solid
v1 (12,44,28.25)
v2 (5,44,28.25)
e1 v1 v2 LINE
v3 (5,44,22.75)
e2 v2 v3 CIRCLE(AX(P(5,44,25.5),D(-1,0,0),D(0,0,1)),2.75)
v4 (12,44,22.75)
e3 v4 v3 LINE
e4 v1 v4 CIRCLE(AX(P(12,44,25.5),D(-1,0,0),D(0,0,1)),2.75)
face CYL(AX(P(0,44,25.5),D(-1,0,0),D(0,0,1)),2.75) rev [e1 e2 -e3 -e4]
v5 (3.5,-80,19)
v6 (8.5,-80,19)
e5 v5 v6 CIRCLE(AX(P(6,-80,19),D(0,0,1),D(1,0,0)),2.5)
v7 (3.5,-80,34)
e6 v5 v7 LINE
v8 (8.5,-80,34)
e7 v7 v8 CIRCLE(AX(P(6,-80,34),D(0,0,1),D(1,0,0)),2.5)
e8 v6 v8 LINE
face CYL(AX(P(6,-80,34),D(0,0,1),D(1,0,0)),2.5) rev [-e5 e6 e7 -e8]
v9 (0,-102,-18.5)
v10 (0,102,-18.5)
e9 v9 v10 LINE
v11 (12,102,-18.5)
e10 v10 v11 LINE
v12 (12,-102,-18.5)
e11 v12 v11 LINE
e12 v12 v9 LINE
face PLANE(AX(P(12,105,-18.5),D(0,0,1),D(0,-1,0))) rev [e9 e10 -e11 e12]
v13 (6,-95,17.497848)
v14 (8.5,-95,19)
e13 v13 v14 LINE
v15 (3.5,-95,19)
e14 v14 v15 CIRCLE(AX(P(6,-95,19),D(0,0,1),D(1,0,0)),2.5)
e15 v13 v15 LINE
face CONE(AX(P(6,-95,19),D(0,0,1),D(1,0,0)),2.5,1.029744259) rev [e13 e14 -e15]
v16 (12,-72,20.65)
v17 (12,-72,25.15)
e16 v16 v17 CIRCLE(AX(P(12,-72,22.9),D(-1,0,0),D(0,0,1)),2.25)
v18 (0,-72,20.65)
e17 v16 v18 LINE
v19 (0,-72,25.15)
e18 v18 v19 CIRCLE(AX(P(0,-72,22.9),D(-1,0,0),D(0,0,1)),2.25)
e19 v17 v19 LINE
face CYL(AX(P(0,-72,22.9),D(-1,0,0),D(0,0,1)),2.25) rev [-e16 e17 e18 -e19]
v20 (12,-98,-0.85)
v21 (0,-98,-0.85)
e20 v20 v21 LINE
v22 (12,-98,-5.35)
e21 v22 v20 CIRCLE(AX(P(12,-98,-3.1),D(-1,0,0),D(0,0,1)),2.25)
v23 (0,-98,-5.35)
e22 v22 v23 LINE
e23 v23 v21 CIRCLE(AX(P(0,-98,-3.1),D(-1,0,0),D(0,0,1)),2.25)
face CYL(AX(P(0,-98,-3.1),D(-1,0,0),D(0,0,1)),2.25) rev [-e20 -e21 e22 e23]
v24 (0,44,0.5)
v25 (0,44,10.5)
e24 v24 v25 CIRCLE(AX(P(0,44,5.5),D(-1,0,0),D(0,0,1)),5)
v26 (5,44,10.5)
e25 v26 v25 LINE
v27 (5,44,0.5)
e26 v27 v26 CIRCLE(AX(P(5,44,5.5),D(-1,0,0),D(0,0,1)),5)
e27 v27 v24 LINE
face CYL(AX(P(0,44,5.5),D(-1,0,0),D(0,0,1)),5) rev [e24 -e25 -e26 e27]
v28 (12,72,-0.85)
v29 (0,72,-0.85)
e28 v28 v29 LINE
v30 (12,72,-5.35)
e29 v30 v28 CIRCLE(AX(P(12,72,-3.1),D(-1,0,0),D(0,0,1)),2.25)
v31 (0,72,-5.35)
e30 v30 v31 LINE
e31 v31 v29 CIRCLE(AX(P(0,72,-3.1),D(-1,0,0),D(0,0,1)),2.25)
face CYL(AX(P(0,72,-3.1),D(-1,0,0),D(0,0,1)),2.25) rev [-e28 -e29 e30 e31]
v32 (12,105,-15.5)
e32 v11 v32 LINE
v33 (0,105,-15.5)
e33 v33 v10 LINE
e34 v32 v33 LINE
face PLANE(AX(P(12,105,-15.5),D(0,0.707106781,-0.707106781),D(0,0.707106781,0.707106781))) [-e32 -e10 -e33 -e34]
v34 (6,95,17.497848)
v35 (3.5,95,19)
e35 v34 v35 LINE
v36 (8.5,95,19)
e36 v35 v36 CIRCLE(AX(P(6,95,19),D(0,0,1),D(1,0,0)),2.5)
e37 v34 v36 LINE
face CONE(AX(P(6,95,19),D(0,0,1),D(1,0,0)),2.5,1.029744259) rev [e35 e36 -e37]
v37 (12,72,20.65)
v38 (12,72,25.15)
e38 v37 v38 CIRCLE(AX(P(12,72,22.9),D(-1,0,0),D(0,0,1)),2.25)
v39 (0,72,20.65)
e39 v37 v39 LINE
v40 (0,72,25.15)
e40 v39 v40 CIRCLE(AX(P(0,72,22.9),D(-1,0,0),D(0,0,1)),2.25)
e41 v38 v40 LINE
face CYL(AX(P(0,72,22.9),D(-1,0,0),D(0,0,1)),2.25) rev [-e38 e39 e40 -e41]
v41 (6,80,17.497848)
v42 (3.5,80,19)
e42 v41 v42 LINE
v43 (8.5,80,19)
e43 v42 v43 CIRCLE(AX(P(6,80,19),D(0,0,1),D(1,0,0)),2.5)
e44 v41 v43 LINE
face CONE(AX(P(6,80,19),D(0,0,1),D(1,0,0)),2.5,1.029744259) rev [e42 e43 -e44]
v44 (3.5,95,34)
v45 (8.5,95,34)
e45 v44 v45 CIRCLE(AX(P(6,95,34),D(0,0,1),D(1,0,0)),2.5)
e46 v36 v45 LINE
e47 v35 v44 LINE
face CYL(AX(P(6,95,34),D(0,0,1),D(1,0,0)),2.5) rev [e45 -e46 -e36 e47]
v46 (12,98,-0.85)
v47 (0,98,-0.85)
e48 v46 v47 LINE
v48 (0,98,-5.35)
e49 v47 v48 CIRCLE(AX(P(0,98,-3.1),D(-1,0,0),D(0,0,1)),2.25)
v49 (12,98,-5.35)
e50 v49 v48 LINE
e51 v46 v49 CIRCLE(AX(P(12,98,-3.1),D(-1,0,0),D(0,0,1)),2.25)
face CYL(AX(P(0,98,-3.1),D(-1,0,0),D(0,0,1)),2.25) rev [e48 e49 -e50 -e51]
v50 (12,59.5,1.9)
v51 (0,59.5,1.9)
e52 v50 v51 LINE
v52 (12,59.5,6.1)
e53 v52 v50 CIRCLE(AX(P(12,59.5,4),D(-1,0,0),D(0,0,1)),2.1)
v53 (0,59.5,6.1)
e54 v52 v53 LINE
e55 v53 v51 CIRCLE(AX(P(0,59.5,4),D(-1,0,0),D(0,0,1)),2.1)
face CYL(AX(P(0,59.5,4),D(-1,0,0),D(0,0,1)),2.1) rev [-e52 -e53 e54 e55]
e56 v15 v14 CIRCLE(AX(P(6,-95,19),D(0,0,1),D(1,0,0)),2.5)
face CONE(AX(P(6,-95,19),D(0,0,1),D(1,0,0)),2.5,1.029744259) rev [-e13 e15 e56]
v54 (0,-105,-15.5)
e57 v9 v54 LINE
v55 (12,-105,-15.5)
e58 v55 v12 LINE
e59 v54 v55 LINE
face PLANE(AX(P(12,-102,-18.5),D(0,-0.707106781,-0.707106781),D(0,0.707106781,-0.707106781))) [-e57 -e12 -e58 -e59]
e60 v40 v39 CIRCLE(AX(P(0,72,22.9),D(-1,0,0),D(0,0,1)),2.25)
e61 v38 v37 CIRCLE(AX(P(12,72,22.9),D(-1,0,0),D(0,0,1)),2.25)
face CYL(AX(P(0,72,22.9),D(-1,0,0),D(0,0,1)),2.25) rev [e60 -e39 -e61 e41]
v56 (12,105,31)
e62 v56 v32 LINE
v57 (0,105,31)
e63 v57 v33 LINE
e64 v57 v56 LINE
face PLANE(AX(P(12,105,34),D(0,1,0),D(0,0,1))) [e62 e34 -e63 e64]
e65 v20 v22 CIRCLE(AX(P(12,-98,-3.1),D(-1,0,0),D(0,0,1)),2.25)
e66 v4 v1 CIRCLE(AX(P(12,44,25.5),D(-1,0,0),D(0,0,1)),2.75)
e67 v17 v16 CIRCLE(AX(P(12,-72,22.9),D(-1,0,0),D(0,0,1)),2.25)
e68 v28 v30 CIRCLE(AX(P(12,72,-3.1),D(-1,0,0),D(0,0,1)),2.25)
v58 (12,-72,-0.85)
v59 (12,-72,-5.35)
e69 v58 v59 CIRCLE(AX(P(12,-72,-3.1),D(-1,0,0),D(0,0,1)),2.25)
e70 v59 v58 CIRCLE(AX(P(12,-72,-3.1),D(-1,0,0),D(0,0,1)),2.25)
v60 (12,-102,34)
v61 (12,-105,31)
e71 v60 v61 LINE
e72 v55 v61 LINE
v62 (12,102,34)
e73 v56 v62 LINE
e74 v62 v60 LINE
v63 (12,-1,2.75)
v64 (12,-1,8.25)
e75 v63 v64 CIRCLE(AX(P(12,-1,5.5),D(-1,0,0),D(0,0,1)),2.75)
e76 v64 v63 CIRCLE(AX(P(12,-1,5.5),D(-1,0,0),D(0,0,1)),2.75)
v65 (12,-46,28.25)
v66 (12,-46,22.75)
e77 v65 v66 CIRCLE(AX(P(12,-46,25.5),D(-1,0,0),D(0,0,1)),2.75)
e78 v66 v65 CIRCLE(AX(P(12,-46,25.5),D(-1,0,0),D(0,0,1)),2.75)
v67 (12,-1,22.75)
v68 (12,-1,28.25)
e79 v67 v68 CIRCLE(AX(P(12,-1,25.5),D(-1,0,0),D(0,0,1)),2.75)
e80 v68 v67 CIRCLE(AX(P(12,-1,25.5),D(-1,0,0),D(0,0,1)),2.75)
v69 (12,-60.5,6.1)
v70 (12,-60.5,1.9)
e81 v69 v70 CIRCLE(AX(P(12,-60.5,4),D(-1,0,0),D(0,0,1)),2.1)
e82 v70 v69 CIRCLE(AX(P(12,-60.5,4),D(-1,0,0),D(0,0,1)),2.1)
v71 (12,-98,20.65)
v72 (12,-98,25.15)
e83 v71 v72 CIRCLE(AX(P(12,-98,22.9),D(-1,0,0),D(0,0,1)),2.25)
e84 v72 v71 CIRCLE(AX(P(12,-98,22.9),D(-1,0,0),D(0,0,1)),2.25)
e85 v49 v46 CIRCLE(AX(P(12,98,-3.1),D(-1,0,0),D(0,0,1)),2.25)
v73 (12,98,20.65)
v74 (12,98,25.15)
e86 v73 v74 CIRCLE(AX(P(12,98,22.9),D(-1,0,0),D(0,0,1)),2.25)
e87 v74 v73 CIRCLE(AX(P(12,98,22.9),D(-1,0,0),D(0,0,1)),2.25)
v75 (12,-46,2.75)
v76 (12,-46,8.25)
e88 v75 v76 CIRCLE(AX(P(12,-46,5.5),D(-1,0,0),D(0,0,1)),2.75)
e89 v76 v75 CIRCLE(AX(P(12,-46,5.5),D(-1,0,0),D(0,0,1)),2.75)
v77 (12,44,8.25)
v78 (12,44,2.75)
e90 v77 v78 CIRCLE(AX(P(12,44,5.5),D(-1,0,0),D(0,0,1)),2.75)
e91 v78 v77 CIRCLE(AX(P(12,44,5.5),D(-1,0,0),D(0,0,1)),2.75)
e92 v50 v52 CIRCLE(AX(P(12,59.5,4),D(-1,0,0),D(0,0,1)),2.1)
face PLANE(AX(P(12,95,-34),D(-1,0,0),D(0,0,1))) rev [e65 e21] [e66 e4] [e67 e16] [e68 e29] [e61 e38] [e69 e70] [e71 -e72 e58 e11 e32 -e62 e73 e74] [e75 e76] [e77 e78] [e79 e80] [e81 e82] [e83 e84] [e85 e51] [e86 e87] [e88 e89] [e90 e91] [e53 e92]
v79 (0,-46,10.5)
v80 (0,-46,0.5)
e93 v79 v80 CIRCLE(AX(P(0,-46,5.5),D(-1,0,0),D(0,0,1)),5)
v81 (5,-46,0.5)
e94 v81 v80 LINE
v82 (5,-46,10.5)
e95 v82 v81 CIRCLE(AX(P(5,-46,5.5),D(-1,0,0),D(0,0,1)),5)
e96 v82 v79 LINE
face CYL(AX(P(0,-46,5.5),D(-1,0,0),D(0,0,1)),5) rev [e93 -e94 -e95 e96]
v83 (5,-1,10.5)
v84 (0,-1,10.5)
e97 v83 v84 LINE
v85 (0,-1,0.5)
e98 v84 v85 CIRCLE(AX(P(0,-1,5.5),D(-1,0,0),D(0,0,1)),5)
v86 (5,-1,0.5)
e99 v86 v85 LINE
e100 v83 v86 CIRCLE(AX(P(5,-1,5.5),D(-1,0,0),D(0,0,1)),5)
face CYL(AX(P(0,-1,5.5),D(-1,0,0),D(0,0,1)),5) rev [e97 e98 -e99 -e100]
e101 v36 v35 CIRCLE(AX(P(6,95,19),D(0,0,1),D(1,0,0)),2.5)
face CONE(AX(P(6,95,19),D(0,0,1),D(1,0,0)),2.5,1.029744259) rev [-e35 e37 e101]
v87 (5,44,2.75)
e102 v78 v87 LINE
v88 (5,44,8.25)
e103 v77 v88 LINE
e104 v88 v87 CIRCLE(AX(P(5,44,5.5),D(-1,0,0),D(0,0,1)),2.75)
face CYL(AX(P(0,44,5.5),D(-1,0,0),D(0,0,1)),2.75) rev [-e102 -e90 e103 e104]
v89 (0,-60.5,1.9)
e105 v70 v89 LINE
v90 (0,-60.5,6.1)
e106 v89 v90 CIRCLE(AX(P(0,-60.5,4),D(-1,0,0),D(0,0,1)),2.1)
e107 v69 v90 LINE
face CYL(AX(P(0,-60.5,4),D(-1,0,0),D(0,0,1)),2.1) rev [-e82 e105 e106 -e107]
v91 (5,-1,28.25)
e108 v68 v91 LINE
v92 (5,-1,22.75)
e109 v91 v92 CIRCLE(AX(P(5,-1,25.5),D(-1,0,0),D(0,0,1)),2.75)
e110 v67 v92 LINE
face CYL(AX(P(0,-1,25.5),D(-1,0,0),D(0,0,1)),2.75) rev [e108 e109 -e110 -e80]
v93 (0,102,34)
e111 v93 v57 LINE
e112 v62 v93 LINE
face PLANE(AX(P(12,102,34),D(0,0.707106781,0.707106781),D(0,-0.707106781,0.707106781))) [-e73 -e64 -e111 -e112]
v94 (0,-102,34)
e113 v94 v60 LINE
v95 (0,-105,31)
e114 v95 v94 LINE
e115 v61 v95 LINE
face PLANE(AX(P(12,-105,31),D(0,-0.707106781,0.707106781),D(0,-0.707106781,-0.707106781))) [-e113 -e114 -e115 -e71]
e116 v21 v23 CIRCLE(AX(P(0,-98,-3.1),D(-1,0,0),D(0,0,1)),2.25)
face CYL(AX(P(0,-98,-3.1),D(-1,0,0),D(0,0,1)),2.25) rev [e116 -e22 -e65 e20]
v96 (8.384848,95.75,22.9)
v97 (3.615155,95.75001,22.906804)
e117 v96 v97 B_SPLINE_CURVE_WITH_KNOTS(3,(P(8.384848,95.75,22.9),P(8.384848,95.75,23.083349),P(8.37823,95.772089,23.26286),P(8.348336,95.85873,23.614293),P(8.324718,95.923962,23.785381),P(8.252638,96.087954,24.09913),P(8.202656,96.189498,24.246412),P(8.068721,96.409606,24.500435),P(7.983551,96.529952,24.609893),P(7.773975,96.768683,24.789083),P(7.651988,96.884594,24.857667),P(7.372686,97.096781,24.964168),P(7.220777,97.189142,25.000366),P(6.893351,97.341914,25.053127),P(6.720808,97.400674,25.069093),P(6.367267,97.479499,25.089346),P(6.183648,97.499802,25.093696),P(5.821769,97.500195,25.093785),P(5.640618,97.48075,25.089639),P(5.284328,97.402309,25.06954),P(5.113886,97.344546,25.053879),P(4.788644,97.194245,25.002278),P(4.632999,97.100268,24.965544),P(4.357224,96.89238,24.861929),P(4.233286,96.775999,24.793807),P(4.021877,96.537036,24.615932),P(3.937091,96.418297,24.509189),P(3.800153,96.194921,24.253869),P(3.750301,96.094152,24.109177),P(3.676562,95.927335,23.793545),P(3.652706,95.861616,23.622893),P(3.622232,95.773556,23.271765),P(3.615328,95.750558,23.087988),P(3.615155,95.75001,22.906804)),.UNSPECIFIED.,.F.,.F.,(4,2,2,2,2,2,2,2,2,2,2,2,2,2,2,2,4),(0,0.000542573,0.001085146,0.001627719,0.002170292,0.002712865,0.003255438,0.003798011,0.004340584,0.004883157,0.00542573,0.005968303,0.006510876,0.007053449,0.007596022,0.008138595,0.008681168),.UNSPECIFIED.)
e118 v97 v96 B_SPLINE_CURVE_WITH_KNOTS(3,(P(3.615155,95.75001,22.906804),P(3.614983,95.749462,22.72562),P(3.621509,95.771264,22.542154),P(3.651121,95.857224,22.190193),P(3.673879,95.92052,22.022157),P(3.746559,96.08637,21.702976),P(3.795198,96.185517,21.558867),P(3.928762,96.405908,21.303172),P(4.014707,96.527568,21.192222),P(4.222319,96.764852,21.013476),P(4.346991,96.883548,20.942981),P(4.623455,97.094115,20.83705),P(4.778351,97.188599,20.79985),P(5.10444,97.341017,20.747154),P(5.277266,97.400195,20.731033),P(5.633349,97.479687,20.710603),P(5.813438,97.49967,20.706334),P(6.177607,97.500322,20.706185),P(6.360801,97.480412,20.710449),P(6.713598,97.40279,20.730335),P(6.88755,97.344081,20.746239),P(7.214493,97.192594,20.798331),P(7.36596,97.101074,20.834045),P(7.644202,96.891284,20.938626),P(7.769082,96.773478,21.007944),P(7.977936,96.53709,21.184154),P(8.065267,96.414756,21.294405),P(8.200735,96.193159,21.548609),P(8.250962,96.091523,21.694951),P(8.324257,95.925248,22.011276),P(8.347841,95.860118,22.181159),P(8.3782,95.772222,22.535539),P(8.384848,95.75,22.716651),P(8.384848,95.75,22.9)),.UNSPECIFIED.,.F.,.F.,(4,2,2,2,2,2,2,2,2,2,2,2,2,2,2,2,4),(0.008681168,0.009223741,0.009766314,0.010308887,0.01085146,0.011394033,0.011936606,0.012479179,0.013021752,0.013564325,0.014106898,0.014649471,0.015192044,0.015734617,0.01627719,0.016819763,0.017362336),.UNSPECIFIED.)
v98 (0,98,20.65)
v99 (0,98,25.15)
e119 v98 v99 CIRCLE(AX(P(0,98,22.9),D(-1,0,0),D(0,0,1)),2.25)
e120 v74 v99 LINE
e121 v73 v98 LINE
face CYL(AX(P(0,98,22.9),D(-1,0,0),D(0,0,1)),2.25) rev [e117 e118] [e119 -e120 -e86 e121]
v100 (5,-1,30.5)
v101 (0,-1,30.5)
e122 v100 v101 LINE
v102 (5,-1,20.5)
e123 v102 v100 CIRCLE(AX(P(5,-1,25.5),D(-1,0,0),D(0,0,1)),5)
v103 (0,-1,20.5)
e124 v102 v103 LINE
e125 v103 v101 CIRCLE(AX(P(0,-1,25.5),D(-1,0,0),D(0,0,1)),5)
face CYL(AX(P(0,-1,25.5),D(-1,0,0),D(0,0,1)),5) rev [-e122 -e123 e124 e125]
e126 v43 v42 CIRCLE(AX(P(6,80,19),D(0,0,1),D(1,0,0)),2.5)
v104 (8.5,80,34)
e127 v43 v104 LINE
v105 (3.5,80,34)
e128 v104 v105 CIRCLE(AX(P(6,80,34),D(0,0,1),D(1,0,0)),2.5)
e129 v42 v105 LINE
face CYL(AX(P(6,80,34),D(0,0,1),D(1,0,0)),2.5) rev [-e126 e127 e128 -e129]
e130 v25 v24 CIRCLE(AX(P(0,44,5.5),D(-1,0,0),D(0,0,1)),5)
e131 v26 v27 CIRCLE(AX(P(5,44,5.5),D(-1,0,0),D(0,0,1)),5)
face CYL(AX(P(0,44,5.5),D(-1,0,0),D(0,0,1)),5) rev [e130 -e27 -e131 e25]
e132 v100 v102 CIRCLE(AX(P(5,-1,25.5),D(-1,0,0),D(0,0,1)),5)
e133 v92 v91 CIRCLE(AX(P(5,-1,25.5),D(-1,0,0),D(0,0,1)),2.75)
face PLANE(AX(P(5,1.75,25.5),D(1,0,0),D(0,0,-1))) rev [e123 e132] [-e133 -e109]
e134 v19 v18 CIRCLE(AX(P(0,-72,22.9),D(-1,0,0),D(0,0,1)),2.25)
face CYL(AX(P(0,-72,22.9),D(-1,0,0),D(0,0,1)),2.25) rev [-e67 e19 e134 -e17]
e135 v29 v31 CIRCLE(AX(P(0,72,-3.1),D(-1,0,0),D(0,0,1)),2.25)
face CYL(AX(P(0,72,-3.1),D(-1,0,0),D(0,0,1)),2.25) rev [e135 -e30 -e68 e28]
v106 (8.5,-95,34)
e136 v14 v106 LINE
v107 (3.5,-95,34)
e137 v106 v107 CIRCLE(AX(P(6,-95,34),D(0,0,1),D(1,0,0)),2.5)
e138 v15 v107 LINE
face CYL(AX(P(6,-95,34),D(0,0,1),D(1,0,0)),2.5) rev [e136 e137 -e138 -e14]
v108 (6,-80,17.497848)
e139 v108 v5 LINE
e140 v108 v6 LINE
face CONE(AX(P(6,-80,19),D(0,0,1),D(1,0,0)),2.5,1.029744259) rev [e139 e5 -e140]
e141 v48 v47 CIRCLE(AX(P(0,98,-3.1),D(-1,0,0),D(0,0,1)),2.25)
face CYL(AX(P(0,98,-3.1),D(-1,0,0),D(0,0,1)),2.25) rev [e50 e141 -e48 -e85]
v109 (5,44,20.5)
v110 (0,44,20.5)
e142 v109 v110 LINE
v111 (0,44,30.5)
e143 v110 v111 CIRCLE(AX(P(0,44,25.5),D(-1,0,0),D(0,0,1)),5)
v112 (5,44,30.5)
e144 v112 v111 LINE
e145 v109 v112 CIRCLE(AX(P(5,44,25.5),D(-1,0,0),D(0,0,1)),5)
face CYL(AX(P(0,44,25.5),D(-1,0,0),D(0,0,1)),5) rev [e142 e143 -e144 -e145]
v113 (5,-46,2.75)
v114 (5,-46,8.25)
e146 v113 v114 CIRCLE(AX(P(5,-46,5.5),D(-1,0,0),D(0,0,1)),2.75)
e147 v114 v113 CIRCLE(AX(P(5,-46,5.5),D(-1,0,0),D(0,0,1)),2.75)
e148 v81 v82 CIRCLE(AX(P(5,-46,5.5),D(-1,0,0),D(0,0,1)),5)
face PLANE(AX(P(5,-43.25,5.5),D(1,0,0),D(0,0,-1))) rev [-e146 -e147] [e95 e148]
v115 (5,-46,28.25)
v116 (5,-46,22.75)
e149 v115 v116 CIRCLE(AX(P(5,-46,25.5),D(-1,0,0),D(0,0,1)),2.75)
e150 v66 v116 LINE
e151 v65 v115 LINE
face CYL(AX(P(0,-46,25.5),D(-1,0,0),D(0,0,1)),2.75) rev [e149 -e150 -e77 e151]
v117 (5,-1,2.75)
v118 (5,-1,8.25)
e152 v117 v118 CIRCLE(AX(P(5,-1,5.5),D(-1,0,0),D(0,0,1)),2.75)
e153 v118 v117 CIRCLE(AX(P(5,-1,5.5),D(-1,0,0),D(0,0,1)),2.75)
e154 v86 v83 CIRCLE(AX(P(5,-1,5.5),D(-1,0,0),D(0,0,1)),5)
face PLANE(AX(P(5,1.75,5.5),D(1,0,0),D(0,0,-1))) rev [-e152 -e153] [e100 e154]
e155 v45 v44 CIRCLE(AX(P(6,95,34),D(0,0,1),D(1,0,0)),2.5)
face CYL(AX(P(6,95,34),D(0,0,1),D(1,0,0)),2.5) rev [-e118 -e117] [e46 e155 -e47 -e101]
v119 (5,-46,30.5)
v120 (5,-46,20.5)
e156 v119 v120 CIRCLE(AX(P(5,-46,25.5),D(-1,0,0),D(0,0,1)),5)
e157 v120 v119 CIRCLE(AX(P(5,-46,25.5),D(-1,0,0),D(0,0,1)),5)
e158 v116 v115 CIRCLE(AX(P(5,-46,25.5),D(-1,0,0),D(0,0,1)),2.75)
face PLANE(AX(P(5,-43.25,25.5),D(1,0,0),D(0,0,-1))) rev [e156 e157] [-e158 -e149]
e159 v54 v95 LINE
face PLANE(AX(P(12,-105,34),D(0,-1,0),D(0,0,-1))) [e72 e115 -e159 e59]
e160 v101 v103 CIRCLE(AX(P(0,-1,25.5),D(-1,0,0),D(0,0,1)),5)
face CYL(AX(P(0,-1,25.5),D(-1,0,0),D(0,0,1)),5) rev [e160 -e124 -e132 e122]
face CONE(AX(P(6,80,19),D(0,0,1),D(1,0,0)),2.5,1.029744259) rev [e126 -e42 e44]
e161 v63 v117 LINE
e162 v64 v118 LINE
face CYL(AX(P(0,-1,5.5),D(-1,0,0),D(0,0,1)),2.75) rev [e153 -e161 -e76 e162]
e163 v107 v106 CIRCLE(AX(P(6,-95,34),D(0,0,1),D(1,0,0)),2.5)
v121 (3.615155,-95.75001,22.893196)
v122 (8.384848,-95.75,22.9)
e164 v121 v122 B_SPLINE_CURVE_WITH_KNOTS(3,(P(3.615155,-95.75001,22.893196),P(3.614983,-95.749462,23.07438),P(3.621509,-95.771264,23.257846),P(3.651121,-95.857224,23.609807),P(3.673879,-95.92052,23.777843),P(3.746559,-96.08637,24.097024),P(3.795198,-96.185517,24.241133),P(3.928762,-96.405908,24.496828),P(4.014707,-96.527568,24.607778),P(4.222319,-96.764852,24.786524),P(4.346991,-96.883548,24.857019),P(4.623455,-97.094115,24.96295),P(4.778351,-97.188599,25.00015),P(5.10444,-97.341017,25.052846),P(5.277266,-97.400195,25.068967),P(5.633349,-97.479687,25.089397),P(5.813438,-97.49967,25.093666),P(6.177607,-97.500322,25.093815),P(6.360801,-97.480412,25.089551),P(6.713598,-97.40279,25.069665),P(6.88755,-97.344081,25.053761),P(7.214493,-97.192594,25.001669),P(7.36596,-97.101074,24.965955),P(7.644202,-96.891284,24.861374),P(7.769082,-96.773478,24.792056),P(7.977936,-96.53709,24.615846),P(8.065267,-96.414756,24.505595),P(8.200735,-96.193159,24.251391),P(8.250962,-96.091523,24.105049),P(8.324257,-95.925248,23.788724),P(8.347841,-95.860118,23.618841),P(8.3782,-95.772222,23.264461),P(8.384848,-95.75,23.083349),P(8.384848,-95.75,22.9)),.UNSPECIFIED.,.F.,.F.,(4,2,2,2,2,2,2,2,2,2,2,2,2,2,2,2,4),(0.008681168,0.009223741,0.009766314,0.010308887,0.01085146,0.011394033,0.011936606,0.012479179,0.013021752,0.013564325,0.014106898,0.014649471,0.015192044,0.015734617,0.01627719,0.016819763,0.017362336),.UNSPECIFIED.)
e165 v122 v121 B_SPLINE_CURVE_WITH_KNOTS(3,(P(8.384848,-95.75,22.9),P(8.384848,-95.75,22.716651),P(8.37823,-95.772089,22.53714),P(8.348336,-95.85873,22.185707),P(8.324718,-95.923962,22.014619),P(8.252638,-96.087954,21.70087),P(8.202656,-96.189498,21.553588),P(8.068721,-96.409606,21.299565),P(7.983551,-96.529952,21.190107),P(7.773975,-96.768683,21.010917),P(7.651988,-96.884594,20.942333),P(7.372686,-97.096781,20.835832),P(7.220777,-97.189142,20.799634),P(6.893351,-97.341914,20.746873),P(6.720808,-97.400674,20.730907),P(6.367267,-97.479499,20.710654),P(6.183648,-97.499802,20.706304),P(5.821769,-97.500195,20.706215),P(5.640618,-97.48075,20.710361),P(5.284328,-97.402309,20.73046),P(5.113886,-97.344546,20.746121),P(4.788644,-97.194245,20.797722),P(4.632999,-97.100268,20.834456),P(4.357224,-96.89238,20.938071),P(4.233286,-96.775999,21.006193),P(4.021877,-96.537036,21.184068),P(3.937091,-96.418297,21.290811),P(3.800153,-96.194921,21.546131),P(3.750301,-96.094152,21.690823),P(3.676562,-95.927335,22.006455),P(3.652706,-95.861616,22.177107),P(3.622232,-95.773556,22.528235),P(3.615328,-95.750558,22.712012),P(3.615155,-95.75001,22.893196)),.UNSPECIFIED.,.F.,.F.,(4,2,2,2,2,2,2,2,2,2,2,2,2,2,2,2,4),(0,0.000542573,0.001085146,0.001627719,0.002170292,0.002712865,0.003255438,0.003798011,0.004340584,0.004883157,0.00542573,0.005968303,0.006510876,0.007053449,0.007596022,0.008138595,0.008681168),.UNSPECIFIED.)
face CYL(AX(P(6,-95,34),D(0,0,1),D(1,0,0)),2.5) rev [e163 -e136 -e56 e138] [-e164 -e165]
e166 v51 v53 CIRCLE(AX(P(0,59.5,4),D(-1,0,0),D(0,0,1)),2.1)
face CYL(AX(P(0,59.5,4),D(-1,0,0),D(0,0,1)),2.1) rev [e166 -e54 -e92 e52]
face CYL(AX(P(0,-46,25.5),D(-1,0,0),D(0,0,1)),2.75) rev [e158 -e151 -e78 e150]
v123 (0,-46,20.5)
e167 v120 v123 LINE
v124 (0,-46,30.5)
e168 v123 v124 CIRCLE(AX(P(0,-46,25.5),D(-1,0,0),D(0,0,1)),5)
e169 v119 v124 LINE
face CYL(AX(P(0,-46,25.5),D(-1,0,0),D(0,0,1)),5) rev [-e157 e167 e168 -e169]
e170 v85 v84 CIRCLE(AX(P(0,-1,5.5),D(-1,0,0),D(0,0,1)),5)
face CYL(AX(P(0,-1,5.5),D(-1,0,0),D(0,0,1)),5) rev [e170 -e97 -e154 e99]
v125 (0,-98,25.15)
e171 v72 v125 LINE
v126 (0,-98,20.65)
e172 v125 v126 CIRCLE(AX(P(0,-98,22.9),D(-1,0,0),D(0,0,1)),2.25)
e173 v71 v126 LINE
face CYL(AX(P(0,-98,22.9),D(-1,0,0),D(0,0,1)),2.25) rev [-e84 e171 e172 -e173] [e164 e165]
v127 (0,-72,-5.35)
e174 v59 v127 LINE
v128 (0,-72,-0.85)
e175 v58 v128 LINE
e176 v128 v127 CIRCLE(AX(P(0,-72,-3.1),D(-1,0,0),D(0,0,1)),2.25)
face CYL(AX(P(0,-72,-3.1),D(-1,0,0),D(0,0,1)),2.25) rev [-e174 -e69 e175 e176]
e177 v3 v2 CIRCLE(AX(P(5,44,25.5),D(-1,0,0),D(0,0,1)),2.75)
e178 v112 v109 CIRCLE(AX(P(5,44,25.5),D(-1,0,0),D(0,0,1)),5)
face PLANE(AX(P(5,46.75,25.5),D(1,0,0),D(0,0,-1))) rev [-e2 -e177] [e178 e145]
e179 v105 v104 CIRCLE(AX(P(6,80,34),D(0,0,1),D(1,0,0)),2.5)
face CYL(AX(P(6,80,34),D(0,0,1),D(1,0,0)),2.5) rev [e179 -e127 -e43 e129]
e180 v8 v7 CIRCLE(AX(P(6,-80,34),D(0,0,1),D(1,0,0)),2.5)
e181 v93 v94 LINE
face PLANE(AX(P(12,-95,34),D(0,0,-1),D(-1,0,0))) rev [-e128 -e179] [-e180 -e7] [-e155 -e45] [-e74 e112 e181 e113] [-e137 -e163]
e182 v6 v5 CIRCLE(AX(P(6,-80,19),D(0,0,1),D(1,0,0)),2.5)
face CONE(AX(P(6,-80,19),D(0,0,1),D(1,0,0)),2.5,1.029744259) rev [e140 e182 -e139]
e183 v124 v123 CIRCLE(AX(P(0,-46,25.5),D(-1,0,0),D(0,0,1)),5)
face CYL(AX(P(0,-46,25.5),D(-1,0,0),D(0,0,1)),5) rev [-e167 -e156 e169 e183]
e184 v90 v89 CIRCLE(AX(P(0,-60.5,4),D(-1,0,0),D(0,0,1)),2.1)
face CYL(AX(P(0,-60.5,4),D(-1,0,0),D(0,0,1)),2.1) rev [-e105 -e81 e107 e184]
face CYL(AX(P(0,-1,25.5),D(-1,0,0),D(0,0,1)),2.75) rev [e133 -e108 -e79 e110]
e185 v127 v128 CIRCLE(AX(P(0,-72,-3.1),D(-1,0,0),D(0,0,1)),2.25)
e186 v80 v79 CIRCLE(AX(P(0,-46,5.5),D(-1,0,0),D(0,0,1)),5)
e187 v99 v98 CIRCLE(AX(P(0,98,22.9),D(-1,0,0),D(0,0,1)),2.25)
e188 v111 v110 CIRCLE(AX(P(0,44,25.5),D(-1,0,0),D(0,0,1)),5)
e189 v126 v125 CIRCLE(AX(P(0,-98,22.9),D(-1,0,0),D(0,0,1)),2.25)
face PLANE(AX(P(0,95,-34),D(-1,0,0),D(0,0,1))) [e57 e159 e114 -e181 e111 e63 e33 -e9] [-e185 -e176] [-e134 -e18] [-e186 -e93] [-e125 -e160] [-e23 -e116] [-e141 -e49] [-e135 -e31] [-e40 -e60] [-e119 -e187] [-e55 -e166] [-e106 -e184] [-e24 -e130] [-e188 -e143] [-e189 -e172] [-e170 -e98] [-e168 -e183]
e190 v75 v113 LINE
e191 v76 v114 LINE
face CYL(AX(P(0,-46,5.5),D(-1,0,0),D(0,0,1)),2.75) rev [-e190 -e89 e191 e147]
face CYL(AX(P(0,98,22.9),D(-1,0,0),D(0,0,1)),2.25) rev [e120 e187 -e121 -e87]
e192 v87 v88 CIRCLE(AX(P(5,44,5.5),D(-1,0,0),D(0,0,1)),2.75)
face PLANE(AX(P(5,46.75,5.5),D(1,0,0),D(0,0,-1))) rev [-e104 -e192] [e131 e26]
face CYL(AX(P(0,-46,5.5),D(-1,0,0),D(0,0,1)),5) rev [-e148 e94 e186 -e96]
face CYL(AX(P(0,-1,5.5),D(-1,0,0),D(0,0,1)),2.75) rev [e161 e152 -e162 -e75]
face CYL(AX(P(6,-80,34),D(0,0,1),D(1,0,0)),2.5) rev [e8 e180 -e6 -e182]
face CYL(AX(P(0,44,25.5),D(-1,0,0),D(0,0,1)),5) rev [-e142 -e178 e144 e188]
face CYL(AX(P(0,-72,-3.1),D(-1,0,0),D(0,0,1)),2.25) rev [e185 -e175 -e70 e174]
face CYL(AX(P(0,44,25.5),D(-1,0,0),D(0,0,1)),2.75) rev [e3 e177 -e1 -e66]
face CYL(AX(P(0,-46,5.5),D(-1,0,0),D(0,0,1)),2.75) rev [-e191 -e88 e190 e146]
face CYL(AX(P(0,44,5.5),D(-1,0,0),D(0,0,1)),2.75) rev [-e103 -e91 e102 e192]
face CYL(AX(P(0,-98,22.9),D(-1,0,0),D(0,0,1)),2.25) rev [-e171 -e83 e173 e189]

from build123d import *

# Parameters (mm, degrees)
SKETCH_1_W                                         = 68
SKETCH_1_H                                         = 190
BOSS_EXTRUDE_1_DEPTH                               = 12
SKETCH_9_W                                         = 68
SKETCH_9_H                                         = 10
BOSS_EXTRUDE_2_DEPTH                               = 12
F_4_5_4_5_HOLE_1_D                                 = 4.5
LINEAR_PATTERN_2_COUNT                             = 2
LINEAR_PATTERN_2_PITCH                             = 26
LINEAR_PATTERN_2_COUNT_DIR2                        = 2
LINEAR_PATTERN_2_PITCH_DIR2                        = 26
M5_SOCKET_HEAD_CAP_SCREW_COUNTERBORE_1_D           = 5.5
M5_SOCKET_HEAD_CAP_SCREW_COUNTERBORE_1_CBORE_D     = 10
M5_SOCKET_HEAD_CAP_SCREW_COUNTERBORE_1_CBORE_DEPTH = 5
LINEAR_PATTERN_3_COUNT                             = 3
LINEAR_PATTERN_3_PITCH                             = 45
LINEAR_PATTERN_3_COUNT_DIR2                        = 2
LINEAR_PATTERN_3_PITCH_DIR2                        = 20
SKETCH_14_W                                        = 20
SKETCH_14_H                                        = 215
CUT_EXTRUDE_4_DEPTH                                = 112.018016556
LINEAR_PATTERN_4_COUNT                             = 2
LINEAR_PATTERN_4_PITCH                             = 170
LINEAR_PATTERN_4_COPY_1_D                          = 4.5
LINEAR_PATTERN_4_COPY_2_D                          = 4.5
LINEAR_PATTERN_4_COPY_3_D                          = 4.5
M5_TAPPED_HOLE_1_D                                 = 4.2
LINEAR_PATTERN_5_COUNT                             = 2
LINEAR_PATTERN_5_PITCH                             = 120
LINEAR_PATTERN_6_COUNT                             = 2
LINEAR_PATTERN_6_PITCH                             = 15
CHAMFER_1_SIZE                                     = 3


with BuildPart() as part:
    # Sketch 1 → Boss-Extrude 1 (new body)
    with BuildSketch(Plane(origin=(0, 0, 0), x_dir=(0, 0, -1), z_dir=(1, 0, 0))):
        Rectangle(SKETCH_1_W, SKETCH_1_H)
    extrude(amount=BOSS_EXTRUDE_1_DEPTH)

    # Sketch 9 → Boss-Extrude 2 (add)
    with BuildSketch(Plane.ZY):
        with Locations((0, 100)):
            Rectangle(SKETCH_9_W, SKETCH_9_H)
        with Locations((0, -100)):
            Rectangle(SKETCH_9_W, SKETCH_9_H)
    extrude(amount=-BOSS_EXTRUDE_2_DEPTH)

    # Ø4.5 (4.5) Hole 1 (through all)
    with Locations(Plane.ZY):
        with Locations((22.9, -98)):
            f_4_5_4_5_hole_1 = Hole(F_4_5_4_5_HOLE_1_D / 2)

    # Linear Pattern 2: 4.5 _4.5_ Hole 1 2 × 2
    with Locations(*[(0, i * LINEAR_PATTERN_2_PITCH, -j * LINEAR_PATTERN_2_PITCH_DIR2) for i in range(LINEAR_PATTERN_2_COUNT) for j in range(LINEAR_PATTERN_2_COUNT_DIR2) if (i, j) != (0, 0)]):
        add(f_4_5_4_5_hole_1, mode=Mode.SUBTRACT)

    # M5 Socket Head Cap Screw Counterbore 1 (through all)
    with Locations(Plane.ZY):
        with Locations((5.5, 44)):
            m5_socket_head_cap_screw_counterbore_1 = CounterBoreHole(M5_SOCKET_HEAD_CAP_SCREW_COUNTERBORE_1_D / 2, M5_SOCKET_HEAD_CAP_SCREW_COUNTERBORE_1_CBORE_D / 2, M5_SOCKET_HEAD_CAP_SCREW_COUNTERBORE_1_CBORE_DEPTH)

    # Linear Pattern 3: M5 Socket Head Cap Screw Counterbore 1 3 × 2
    with Locations(*[(0, -i * LINEAR_PATTERN_3_PITCH, j * LINEAR_PATTERN_3_PITCH_DIR2) for i in range(LINEAR_PATTERN_3_COUNT) for j in range(LINEAR_PATTERN_3_COUNT_DIR2) if (i, j) != (0, 0)]):
        add(m5_socket_head_cap_screw_counterbore_1, mode=Mode.SUBTRACT)

    # Sketch 14 → Cut-Extrude 4 (cut, through all)
    with BuildSketch(Plane.ZY):
        with Locations((-28.5, -2.5)):
            Rectangle(SKETCH_14_W, SKETCH_14_H)
    extrude(amount=-CUT_EXTRUDE_4_DEPTH, mode=Mode.SUBTRACT)

    # Linear Pattern 4: Ø4.5 (4.5) Hole 1 ×2
    with Locations(*[(0, i * LINEAR_PATTERN_4_PITCH, 0) for i in range(1, LINEAR_PATTERN_4_COUNT)]):
        add(f_4_5_4_5_hole_1, mode=Mode.SUBTRACT)

    # Linear Pattern 4 copy 1 (through all)
    with Locations(Plane(origin=(0, 170, -26), x_dir=(0, 0, 1), z_dir=(-1, 0, 0))):
        with Locations((22.9, -98)):
            Hole(LINEAR_PATTERN_4_COPY_1_D / 2)

    # Linear Pattern 4 copy 2 (through all)
    with Locations(Plane(origin=(0, 196, 0), x_dir=(0, 0, 1), z_dir=(-1, 0, 0))):
        with Locations((22.9, -98)):
            Hole(LINEAR_PATTERN_4_COPY_2_D / 2)

    # Linear Pattern 4 copy 3 (through all)
    with Locations(Plane(origin=(0, 196, -26), x_dir=(0, 0, 1), z_dir=(-1, 0, 0))):
        with Locations((22.9, -98)):
            Hole(LINEAR_PATTERN_4_COPY_3_D / 2)

    # M5 Tapped Hole 1 (through all)
    with Locations(Plane.ZY):
        with Locations((4, 59.5)):
            m5_tapped_hole_1 = Hole(M5_TAPPED_HOLE_1_D / 2)

    # Linear Pattern 5: M5 Tapped Hole 1 ×2
    with Locations(*[(0, -i * LINEAR_PATTERN_5_PITCH, 0) for i in range(1, LINEAR_PATTERN_5_COUNT)]):
        add(m5_tapped_hole_1, mode=Mode.SUBTRACT)

    # Sketch 17 → M6 Tapped Hole 1 (revolve, cut)
    with BuildSketch(Plane(origin=(6, 95, 34), x_dir=(0, -1, 0), z_dir=(1, 0, 0))):
        Polygon((0, 0), (0, 16.502151548), (2.5, 15), (2.5, 0), align=None)
    m6_tapped_hole_1 = revolve(axis=Axis((6, 95, 40.35), (0, 0, -1)), mode=Mode.SUBTRACT)

    # Linear Pattern 6: M6 Tapped Hole 1 ×2
    with Locations(*[(0, -i * LINEAR_PATTERN_6_PITCH, 0) for i in range(1, LINEAR_PATTERN_6_COUNT)]):
        add(m6_tapped_hole_1, mode=Mode.SUBTRACT)

    # Mirror 1: M6 Tapped Hole 1 across plane
    add(m6_tapped_hole_1.mirror(Plane.ZX), mode=Mode.SUBTRACT)

    # Mirror 1 copy 1 sketch → Mirror 1 copy 1 (revolve, cut)
    with BuildSketch(Plane(origin=(6, -80, 34), x_dir=(0, 1, 0), z_dir=(1, 0, 0))):
        Polygon((0, 0), (0, -16.502151548), (2.5, -15), (2.5, 0), align=None)
    revolve(axis=Axis((6, -80, 40.35), (0, 0, 1)), mode=Mode.SUBTRACT)

    # Chamfer 1
    chamfer_1_edges = [part.edges().sort_by_distance(p)[0] for p in [
        (6, 105, 34),
        (6, -105, 34),
        (6, -105, -18.5),
        (6, 105, -18.5),
    ]]
    chamfer(chamfer_1_edges, length=CHAMFER_1_SIZE)


solid = part.part
